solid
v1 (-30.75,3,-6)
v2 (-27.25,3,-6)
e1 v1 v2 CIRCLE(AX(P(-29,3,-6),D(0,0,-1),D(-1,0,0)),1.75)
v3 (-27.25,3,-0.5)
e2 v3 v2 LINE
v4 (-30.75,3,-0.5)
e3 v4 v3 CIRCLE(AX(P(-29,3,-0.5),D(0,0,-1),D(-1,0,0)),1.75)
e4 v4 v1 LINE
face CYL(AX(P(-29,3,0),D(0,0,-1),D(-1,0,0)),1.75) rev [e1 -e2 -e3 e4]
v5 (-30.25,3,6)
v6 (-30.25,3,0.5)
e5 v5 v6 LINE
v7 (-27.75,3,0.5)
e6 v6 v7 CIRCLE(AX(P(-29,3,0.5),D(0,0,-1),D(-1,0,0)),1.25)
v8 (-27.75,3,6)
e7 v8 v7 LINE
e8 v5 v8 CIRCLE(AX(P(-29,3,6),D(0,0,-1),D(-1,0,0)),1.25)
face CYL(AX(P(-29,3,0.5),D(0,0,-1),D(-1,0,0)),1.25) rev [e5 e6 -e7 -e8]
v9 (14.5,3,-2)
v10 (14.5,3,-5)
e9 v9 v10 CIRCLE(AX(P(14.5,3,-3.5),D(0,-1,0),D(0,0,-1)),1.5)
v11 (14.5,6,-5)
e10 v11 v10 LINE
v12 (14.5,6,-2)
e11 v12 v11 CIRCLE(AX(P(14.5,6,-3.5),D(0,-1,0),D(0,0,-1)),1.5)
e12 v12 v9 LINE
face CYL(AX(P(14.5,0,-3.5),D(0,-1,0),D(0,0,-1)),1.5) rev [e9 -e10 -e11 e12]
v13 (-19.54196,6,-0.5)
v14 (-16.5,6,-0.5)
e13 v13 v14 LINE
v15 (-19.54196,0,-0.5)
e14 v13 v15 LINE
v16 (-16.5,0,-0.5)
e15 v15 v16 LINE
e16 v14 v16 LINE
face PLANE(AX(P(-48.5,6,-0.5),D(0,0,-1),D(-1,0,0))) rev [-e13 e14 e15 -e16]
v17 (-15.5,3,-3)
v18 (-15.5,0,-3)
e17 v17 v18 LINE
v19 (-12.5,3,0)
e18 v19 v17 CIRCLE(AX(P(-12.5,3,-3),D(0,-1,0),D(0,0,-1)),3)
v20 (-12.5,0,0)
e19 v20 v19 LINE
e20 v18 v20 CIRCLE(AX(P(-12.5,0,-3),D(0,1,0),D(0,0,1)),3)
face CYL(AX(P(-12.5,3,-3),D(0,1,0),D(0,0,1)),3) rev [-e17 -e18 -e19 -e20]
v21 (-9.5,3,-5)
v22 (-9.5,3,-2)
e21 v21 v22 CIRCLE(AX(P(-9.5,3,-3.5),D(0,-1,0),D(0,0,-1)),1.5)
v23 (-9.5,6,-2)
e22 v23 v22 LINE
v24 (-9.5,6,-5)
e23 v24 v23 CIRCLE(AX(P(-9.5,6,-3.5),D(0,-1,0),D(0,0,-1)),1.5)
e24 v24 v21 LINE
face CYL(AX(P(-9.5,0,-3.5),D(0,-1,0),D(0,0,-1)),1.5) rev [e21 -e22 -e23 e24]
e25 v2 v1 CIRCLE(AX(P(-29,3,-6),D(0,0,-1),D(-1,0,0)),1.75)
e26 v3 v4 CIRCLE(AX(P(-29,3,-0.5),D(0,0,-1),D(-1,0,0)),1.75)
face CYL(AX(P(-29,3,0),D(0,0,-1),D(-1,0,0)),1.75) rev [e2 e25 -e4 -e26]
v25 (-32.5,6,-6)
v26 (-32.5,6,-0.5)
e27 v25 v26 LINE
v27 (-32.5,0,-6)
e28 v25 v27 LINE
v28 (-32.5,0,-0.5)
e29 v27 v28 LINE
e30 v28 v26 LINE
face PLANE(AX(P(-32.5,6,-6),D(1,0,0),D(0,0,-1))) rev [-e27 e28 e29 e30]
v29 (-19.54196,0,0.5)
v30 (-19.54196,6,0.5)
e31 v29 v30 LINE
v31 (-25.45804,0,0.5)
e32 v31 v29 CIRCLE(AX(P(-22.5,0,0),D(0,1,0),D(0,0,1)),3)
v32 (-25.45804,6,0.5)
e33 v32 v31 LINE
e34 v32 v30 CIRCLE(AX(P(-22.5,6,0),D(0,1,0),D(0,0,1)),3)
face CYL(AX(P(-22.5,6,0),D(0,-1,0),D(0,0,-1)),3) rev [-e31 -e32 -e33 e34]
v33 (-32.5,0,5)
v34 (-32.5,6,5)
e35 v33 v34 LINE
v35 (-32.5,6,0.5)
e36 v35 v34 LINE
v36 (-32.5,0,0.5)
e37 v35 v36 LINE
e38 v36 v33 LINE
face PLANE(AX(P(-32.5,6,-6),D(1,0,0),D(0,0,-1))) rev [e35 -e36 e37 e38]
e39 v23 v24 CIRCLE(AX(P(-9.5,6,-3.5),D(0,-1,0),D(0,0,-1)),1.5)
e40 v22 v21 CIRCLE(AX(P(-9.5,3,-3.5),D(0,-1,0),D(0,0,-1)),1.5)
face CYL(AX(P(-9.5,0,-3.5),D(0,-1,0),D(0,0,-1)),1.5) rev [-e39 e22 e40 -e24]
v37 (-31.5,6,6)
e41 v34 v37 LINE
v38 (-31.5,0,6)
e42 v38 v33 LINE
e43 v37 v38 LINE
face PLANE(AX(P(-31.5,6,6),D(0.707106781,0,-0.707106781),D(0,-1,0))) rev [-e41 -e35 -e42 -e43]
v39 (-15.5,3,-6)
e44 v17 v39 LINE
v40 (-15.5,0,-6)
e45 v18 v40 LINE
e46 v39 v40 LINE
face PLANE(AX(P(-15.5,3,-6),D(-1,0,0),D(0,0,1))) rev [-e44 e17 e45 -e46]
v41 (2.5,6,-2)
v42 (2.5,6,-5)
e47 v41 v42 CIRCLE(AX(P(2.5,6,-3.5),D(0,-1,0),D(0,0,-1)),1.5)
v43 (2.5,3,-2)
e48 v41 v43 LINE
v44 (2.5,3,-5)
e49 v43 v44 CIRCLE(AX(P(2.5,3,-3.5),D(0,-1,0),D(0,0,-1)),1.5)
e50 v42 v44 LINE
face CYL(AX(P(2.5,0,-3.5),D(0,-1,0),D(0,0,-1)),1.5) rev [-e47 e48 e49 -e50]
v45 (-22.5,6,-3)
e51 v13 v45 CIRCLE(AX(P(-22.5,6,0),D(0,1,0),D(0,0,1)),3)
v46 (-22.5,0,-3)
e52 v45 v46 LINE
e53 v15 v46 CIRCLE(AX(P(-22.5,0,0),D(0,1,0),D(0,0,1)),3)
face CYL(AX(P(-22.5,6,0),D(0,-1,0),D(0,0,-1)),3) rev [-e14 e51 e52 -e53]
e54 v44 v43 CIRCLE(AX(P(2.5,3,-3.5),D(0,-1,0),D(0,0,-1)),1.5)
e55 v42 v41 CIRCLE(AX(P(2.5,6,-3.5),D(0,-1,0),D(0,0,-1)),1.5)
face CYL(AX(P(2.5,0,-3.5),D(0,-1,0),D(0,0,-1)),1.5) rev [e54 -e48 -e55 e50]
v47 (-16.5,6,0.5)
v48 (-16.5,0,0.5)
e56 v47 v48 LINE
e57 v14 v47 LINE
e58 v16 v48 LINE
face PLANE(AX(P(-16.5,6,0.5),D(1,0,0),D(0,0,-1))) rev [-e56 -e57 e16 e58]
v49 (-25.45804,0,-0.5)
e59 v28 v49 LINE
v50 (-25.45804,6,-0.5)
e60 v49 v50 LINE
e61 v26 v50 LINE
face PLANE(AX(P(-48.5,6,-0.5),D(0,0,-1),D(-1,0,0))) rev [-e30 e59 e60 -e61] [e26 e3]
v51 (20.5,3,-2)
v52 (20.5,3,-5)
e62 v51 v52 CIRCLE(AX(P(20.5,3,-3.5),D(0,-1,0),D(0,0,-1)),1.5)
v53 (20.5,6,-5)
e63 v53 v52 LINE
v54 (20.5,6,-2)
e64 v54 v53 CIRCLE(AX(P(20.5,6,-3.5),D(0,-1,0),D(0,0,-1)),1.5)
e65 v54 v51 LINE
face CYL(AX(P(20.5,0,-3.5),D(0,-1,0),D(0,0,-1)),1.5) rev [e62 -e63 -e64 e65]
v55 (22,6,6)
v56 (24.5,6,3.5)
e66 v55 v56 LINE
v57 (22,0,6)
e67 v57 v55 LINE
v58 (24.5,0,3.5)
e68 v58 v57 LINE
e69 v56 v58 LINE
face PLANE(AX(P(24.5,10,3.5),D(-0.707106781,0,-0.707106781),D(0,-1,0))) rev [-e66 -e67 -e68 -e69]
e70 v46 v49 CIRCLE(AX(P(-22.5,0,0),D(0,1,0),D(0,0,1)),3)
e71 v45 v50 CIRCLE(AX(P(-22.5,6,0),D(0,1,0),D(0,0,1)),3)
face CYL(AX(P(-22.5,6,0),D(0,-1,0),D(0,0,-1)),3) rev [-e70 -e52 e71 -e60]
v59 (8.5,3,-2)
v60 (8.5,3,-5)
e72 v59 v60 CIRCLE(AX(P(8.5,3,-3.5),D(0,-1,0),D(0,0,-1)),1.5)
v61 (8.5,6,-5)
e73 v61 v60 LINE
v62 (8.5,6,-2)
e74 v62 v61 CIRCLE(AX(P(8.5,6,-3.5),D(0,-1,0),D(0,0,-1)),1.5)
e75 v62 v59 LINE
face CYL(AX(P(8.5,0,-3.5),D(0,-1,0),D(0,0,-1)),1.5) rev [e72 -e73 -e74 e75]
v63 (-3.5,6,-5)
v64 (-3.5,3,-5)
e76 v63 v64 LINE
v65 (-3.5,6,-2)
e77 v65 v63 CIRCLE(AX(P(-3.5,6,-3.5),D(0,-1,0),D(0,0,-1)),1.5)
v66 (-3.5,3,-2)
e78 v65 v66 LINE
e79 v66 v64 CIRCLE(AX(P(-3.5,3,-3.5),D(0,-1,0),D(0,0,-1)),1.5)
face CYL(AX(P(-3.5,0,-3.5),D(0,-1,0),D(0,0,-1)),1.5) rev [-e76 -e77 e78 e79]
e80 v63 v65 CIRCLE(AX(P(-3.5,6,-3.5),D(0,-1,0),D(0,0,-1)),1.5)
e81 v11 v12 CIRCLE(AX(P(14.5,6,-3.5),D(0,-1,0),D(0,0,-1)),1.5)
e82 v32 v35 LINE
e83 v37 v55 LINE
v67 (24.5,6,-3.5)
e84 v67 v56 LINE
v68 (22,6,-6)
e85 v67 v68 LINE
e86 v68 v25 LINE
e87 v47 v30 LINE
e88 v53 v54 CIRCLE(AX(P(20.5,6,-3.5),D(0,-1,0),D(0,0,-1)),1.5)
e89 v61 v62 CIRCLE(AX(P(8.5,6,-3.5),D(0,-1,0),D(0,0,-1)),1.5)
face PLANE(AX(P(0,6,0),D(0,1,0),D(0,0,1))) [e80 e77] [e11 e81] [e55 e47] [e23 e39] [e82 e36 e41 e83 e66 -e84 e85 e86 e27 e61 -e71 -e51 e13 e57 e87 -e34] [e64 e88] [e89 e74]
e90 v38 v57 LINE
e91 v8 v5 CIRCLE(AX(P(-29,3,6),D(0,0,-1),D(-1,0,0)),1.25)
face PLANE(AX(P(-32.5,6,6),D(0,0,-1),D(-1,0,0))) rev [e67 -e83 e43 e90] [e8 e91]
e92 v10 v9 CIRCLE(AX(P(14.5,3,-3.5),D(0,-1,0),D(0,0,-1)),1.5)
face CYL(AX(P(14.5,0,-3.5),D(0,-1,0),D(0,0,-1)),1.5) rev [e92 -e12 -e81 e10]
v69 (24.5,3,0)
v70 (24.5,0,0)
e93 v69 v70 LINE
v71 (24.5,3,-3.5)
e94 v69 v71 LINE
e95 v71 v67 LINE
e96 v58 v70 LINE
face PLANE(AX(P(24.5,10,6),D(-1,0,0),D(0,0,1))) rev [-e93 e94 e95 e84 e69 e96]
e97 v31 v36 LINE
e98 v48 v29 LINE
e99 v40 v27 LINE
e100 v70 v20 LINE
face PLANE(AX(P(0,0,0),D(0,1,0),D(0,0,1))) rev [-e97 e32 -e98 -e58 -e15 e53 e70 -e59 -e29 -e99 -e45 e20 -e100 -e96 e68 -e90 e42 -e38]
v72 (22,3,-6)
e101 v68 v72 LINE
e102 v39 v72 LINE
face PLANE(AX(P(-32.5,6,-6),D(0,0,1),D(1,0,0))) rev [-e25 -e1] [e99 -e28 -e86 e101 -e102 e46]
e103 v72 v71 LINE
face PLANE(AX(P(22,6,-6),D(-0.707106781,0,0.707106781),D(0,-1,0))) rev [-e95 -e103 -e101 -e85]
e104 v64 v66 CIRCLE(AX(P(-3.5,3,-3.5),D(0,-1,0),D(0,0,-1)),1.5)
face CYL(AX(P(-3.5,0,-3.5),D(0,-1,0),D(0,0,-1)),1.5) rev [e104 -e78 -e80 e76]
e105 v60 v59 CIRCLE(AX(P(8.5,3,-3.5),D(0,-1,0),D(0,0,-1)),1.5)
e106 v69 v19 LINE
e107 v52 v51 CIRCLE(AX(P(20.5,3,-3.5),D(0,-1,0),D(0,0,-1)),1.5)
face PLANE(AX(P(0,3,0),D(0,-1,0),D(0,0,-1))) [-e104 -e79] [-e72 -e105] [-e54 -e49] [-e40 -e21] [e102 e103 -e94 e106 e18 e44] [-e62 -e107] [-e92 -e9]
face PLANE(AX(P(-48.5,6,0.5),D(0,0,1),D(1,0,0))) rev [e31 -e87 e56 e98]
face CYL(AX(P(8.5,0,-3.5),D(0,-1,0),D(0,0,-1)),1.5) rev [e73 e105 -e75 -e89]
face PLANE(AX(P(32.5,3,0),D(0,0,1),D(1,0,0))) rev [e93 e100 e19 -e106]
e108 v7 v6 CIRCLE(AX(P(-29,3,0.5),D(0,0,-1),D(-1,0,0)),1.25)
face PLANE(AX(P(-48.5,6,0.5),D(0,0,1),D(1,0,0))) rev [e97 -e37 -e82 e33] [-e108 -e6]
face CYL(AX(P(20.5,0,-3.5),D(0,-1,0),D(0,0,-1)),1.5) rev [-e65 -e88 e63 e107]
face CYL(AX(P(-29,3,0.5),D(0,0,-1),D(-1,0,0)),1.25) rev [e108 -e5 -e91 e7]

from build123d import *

# Parameters (mm, degrees)
SKETCH1_W                = 65
SKETCH1_H                = 12
SKETCH1_R                = 3
BOSS_EXTRUDE1_DEPTH      = 6
SKETCH2_W                = 32
SKETCH2_H                = 1
CUT_EXTRUDE1_DEPTH       = 34.589432862
SKETCH4_R                = 1.75
CUT_EXTRUDE3_DEPTH       = 6
M3_TAPPED_HOLE1_D        = 2.5
SKETCH10_W               = 48
SKETCH10_H               = 6
CUT_EXTRUDE4_DEPTH       = 3
F_3_0_3_DIAMETER_HOLE1_D = 3
LPATTERN1_COUNT          = 6
LPATTERN1_PITCH          = 6
FILLET1_R                = 3
SKETCH11_W               = 8
SKETCH11_H               = 12
CUT_EXTRUDE5_DEPTH       = 10
CHAMFER1_SIZE            = 1
CHAMFER2_SIZE            = 2.5


with BuildPart() as part:
    # Sketch1 → Boss-Extrude1 (new body)
    with BuildSketch(Plane(origin=(0, 0, 0), x_dir=(1, 0, 0), z_dir=(0, 1, 0))):
        Rectangle(SKETCH1_W, SKETCH1_H)
        with Locations(Location((-22.5, 0, 0), (0, 0, 270))):
            Circle(SKETCH1_R, mode=Mode.SUBTRACT)
    extrude(amount=BOSS_EXTRUDE1_DEPTH)

    # Sketch2 → Cut-Extrude1 (cut, through all)
    with BuildSketch(Plane.XZ):
        with Locations((-32.5, 0)):
            Rectangle(SKETCH2_W, SKETCH2_H)
    extrude(amount=-CUT_EXTRUDE1_DEPTH, mode=Mode.SUBTRACT)

    # Sketch4 → Cut-Extrude3 (cut)
    with BuildSketch(Plane(origin=(0, 0, -6), x_dir=(-1, 0, 0), z_dir=(0, 0, -1))):
        with Locations((29, 3)):
            Circle(SKETCH4_R)
    extrude(amount=-CUT_EXTRUDE3_DEPTH, mode=Mode.SUBTRACT)

    # M3 Tapped Hole1 (through all)
    with Locations(Plane(origin=(-29, 3, 0.5), x_dir=(-1, 0, 0), z_dir=(0, 0, -1))):
        with Locations((0, 0)):
            Hole(M3_TAPPED_HOLE1_D / 2)

    # Sketch10 → Cut-Extrude4 (cut)
    with BuildSketch(Plane.XZ):
        with Locations((8.5, -3)):
            Rectangle(SKETCH10_W, SKETCH10_H)
    extrude(amount=-CUT_EXTRUDE4_DEPTH, mode=Mode.SUBTRACT)

    # Ø3.0 (3) Diameter Hole1 (through all)
    with Locations(Plane(origin=(20.5, 0, -3.5), x_dir=(0, 0, -1), z_dir=(0, -1, 0))):
        with Locations((0, 0)):
            f_3_0_3_diameter_hole1 = Hole(F_3_0_3_DIAMETER_HOLE1_D / 2)

    # LPattern1: Ø3.0 (3) Diameter Hole1 ×6
    with Locations(*[(-i * LPATTERN1_PITCH, 0, 0) for i in range(1, LPATTERN1_COUNT)]):
        add(f_3_0_3_diameter_hole1, mode=Mode.SUBTRACT)

    # Fillet1
    fillet1_edges = [part.edges().sort_by_distance(p)[0] for p in [
        (-15.5, 1.5, 0),
    ]]
    fillet(fillet1_edges, radius=FILLET1_R)

    # Sketch11 → Cut-Extrude5 (cut)
    with BuildSketch(Plane.XZ):
        with Locations((28.5, 0)):
            Rectangle(SKETCH11_W, SKETCH11_H)
    extrude(amount=-CUT_EXTRUDE5_DEPTH, mode=Mode.SUBTRACT)

    # Chamfer1
    chamfer1_edges = [part.edges().sort_by_distance(p)[0] for p in [
        (-32.5, 3, 6),
    ]]
    chamfer(chamfer1_edges, length=CHAMFER1_SIZE)

    # Chamfer2
    chamfer2_edges = [part.edges().sort_by_distance(p)[0] for p in [
        (24.5, 4.5, -6),
        (24.5, 3, 6),
    ]]
    chamfer(chamfer2_edges, length=CHAMFER2_SIZE)


solid = part.part
